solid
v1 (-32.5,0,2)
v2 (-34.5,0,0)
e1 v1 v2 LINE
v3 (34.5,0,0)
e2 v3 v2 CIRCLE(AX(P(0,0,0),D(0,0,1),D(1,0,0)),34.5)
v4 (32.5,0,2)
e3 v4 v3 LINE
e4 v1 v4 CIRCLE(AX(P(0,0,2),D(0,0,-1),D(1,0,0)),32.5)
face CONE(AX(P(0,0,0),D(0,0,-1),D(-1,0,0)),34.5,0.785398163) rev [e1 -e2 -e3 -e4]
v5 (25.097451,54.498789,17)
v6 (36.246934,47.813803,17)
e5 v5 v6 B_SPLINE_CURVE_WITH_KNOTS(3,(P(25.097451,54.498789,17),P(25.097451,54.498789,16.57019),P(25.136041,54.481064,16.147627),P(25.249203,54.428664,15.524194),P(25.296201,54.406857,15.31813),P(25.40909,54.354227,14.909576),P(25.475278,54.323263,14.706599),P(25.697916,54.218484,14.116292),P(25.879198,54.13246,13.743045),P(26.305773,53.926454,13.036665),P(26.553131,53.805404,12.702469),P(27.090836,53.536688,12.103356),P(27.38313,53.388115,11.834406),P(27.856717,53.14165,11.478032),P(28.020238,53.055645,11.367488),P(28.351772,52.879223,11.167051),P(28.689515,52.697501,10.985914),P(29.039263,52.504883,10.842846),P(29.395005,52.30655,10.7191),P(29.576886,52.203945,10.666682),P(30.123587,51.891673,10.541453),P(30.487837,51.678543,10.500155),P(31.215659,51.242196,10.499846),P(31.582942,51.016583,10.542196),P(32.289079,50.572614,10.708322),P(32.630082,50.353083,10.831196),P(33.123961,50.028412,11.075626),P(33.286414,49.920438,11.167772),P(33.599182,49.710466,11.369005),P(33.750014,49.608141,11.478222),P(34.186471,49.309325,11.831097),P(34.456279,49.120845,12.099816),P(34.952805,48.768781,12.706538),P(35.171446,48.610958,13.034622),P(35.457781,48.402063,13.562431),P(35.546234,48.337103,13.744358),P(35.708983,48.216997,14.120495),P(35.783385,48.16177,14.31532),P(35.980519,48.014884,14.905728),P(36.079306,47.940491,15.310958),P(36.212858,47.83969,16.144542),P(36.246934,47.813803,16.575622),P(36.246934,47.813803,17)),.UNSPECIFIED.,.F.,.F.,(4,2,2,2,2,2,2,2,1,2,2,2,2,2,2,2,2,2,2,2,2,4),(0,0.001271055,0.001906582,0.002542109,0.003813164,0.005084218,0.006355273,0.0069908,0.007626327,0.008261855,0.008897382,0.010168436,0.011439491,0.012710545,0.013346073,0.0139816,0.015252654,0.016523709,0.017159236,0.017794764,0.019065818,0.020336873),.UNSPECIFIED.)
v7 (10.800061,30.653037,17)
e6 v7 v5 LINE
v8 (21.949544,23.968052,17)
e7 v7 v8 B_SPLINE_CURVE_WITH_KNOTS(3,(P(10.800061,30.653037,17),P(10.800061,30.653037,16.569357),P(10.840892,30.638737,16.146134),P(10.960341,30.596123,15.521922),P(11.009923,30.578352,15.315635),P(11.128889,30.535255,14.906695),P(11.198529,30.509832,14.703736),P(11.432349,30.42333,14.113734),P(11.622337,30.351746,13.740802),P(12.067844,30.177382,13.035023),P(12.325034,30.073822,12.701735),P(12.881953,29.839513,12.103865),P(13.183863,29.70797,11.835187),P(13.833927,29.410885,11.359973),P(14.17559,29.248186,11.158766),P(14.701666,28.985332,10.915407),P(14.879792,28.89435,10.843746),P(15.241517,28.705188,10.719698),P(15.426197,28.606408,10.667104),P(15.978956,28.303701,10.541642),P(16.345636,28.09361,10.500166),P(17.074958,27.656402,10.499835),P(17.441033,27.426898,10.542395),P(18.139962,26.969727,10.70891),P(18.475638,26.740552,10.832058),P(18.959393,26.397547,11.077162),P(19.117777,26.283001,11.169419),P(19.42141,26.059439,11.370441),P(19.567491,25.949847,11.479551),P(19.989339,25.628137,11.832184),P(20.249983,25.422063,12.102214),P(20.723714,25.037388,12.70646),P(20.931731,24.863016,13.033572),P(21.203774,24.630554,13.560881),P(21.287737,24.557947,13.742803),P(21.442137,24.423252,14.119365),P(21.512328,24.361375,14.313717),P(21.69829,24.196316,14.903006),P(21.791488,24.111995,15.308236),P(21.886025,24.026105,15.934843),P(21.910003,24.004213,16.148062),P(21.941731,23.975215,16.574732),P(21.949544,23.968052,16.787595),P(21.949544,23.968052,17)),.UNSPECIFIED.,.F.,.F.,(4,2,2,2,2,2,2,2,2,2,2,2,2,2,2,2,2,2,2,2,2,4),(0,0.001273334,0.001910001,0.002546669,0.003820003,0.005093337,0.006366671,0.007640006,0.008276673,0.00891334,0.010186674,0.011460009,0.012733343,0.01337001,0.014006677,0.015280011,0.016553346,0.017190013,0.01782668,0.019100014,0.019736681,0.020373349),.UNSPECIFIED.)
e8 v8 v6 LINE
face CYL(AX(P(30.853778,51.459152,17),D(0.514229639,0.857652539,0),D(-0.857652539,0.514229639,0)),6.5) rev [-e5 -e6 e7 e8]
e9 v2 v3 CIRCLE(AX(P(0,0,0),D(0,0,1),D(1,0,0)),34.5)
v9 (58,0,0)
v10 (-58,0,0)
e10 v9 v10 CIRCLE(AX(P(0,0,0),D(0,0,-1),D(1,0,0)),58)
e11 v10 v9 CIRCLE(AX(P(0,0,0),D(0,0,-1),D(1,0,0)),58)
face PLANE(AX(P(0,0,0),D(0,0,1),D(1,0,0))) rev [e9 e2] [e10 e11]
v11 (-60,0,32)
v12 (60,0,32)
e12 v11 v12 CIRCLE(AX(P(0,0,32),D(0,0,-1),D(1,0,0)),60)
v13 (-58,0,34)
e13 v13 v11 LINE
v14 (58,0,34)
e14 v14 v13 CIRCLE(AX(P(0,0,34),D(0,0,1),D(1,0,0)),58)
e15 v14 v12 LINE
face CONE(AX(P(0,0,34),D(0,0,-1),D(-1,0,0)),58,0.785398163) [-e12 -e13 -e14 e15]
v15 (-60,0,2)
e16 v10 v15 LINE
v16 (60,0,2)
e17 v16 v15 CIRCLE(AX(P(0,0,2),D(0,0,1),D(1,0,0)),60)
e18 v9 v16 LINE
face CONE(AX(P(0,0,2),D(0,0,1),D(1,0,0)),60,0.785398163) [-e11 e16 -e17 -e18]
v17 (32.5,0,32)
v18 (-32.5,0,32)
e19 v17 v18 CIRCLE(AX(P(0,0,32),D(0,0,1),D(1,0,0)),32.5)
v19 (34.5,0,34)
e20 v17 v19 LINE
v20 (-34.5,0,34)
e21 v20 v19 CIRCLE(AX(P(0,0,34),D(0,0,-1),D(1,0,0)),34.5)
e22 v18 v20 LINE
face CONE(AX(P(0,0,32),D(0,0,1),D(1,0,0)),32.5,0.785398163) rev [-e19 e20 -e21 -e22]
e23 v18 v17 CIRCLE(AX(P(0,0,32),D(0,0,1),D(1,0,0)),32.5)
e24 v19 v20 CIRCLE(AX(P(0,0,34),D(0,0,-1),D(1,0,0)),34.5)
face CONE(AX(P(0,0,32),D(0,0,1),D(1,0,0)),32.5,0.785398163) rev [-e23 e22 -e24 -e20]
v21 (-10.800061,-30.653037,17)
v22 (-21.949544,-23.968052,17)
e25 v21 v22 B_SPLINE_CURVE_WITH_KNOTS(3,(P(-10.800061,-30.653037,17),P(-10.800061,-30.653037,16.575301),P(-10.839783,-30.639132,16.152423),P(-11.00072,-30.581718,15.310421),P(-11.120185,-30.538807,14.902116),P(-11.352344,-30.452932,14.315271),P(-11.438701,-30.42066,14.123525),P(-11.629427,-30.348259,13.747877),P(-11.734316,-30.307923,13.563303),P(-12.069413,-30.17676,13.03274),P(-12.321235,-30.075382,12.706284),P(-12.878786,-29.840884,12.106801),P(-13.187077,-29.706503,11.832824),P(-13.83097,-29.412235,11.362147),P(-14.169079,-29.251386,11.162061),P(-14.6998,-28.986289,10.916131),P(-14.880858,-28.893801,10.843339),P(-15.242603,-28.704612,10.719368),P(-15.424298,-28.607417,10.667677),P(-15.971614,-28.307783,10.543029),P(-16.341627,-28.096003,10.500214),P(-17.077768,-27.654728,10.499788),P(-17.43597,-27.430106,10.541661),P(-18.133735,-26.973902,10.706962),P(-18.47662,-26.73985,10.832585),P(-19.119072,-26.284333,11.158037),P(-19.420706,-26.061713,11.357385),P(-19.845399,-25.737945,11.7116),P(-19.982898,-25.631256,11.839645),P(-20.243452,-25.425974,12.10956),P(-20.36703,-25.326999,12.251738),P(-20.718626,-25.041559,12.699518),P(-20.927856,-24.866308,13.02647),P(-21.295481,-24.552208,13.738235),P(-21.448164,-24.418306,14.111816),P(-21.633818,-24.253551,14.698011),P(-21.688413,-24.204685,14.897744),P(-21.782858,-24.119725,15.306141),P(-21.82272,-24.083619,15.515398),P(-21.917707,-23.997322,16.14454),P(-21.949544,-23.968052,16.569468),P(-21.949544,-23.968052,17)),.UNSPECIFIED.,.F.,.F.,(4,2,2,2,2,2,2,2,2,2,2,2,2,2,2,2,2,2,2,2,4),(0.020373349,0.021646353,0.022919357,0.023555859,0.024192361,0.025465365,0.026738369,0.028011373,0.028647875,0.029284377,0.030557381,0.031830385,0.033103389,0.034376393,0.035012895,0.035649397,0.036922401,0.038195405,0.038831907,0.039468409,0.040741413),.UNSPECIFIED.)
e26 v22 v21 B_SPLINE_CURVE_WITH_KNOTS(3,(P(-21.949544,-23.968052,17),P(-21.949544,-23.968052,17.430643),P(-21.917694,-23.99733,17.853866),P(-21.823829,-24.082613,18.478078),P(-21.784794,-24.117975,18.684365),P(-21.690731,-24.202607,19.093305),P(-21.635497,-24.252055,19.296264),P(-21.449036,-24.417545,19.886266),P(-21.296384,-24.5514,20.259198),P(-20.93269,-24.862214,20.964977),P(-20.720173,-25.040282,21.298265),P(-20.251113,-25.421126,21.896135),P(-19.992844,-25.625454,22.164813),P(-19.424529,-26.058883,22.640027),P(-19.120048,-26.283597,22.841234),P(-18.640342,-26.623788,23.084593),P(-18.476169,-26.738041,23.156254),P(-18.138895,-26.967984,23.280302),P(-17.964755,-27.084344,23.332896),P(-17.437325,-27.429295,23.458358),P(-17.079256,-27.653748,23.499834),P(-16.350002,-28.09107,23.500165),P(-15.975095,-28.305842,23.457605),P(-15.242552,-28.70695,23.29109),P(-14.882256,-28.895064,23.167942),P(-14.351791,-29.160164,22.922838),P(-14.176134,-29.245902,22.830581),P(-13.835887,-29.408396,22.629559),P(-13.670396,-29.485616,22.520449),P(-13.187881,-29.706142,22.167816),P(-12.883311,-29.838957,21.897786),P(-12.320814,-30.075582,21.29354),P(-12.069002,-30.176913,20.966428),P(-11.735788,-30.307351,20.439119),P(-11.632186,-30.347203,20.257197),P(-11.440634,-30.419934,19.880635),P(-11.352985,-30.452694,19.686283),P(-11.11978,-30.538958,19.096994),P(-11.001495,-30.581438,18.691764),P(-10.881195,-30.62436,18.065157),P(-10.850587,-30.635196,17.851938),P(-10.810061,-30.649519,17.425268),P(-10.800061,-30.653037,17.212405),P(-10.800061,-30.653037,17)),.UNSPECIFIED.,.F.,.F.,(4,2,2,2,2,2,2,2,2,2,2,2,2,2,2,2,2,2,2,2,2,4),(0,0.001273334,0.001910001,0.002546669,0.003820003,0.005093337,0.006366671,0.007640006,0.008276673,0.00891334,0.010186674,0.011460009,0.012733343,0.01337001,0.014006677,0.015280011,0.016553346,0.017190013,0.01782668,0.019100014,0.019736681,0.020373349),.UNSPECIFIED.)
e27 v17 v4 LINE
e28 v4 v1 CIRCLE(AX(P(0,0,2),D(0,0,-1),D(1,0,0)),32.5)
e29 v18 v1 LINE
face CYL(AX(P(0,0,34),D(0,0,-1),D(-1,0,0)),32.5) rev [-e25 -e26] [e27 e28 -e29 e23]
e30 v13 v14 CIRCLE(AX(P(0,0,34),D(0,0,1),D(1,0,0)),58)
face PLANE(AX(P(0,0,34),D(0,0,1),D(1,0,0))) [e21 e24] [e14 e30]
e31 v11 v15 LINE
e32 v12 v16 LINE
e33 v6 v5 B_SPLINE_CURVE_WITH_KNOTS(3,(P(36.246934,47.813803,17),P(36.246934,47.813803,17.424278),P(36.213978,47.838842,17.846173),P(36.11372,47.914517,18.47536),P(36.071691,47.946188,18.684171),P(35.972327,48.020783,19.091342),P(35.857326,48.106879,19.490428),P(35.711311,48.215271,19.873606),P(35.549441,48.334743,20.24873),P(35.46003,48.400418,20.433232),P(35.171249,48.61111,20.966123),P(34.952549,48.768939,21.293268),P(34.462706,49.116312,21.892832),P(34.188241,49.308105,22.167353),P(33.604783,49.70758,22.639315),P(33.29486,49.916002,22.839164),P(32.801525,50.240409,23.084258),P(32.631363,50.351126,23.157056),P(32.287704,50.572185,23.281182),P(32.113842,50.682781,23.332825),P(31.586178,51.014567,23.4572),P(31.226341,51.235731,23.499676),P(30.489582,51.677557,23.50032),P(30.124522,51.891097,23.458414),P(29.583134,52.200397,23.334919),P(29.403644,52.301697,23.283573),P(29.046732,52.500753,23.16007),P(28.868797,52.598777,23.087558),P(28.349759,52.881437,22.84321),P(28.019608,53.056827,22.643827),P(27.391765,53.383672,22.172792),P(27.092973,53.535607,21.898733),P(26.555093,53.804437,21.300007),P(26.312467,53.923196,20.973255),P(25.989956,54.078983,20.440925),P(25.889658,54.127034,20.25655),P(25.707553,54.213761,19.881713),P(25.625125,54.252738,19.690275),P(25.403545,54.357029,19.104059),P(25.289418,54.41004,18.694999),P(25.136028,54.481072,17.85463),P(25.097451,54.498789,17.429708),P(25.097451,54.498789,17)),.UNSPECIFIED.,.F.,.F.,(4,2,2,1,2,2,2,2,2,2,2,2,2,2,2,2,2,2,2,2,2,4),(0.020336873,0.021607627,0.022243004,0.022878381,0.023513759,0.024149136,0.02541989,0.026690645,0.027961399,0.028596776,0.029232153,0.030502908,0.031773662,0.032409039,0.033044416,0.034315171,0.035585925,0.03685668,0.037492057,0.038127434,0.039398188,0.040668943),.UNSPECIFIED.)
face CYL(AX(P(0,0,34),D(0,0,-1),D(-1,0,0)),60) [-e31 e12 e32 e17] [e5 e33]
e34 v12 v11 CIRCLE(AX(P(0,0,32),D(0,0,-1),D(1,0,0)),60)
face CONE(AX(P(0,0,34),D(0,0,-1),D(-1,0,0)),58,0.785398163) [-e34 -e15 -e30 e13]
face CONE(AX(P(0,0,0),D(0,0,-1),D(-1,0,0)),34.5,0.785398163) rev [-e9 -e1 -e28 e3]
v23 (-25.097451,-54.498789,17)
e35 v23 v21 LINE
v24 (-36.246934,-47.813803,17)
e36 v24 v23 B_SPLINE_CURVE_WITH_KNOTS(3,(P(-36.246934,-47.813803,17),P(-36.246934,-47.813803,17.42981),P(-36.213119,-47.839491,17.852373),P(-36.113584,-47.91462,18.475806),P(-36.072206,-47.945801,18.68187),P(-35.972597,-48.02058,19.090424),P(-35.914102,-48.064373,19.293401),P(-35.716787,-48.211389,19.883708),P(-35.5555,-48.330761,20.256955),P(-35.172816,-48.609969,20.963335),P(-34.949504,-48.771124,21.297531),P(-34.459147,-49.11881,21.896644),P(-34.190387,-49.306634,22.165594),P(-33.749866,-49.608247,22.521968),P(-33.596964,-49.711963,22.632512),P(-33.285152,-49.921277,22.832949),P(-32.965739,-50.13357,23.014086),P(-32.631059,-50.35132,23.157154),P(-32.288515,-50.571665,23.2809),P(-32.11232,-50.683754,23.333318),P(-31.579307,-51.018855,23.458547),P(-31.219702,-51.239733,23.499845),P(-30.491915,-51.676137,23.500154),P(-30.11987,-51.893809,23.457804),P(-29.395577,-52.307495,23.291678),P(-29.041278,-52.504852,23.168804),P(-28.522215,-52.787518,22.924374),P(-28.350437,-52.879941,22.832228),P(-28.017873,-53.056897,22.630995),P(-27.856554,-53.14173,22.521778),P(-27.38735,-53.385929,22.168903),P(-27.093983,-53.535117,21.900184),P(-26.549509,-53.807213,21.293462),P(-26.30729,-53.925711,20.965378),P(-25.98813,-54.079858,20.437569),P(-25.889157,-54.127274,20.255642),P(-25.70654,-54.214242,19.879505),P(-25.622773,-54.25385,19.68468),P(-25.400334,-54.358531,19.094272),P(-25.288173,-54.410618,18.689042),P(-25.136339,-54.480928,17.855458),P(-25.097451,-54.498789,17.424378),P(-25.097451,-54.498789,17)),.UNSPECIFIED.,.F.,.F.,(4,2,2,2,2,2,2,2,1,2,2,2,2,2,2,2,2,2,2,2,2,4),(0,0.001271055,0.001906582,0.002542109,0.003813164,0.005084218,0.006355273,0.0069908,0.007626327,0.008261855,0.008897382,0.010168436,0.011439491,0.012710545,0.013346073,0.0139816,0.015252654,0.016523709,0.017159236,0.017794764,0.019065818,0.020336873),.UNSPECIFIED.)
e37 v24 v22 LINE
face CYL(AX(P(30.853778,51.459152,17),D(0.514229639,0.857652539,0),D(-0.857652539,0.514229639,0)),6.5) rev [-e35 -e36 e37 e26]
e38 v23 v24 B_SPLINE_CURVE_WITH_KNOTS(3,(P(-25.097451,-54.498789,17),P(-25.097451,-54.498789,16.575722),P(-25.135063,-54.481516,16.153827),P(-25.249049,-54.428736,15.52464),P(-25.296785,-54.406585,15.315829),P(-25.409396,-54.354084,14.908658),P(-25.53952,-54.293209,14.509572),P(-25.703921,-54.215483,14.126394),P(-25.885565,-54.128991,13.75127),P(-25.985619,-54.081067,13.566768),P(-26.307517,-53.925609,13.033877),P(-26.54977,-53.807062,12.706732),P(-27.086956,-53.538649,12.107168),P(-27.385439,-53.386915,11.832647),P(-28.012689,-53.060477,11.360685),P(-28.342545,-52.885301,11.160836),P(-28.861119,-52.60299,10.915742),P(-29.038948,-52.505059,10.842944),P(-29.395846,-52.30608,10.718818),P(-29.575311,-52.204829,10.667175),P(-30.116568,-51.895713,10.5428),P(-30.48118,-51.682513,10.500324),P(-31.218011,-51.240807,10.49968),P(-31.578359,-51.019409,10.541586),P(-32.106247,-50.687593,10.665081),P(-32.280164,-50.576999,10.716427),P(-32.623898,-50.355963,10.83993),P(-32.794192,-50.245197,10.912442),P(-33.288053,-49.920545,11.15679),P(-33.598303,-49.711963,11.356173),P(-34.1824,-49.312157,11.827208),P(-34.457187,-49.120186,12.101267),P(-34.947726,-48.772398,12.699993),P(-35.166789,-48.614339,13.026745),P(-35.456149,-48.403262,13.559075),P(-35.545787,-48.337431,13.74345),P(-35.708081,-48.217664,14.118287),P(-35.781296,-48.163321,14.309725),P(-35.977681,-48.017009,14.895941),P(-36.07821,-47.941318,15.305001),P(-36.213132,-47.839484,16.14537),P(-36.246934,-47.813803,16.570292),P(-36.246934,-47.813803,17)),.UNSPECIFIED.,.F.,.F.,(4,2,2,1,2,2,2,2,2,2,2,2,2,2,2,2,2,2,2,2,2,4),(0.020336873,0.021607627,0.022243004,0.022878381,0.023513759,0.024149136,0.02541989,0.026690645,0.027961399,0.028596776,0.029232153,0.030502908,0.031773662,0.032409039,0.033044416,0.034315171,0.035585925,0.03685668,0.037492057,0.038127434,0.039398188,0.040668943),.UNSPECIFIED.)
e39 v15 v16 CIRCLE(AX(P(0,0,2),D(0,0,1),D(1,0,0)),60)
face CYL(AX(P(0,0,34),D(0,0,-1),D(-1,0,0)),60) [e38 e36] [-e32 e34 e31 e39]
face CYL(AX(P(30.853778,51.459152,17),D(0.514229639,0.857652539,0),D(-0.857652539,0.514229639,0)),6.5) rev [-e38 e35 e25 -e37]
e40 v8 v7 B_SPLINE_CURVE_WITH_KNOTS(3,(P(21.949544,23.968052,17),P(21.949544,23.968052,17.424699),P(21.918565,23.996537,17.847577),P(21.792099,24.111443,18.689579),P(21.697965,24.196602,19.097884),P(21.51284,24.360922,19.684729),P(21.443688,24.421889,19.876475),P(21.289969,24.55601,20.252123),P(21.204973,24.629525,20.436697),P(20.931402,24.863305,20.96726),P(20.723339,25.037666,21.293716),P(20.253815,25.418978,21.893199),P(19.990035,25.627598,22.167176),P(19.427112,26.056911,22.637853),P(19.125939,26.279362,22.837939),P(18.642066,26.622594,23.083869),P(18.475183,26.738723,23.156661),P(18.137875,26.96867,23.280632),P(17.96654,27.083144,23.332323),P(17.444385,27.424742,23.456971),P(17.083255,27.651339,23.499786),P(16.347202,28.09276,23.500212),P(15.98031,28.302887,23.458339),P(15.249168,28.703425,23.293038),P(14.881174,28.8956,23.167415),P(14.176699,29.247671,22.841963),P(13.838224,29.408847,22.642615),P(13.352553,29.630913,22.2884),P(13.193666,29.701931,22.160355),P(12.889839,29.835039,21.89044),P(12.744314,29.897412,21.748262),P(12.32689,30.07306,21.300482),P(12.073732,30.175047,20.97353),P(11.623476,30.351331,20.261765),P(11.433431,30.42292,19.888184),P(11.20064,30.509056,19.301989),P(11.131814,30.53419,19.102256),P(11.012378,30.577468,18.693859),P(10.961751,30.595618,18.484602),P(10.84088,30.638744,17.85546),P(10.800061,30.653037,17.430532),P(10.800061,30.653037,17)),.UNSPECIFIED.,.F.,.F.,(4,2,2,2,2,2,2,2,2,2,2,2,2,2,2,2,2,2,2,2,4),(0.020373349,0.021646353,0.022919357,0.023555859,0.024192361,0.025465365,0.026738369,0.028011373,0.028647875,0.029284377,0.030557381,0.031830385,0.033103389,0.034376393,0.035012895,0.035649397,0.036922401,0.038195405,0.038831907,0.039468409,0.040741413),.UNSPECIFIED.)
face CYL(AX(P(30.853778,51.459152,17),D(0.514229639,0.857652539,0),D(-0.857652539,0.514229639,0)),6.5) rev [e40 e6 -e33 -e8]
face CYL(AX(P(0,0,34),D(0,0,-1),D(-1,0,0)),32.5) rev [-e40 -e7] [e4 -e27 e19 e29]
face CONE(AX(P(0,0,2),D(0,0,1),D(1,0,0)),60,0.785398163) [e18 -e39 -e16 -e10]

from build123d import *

# Parameters (mm, degrees)
SKETCH1_R                  = 60
SKETCH1_R_2                = 32.5
BOSS_EXTRUDE1_DEPTH        = 34
F_13_0_13_DIAMETER_HOLE1_D = 13
CHAMFER1_SIZE              = 2


with BuildPart() as part:
    # Sketch1 → Boss-Extrude1 (new body)
    with BuildSketch(Plane.XY):
        Circle(SKETCH1_R)
        Circle(SKETCH1_R_2, mode=Mode.SUBTRACT)
    extrude(amount=BOSS_EXTRUDE1_DEPTH)

    # Ø13.0 (13) Diameter Hole1 (through all)
    with Locations(Plane(origin=(30.853778368, 51.459152348, 17), x_dir=(0.85765253914, -0.514229639467, 0), z_dir=(0.514229639467, 0.85765253914, 0))):
        with Locations((0, 0)):
            Hole(F_13_0_13_DIAMETER_HOLE1_D / 2)

    # Chamfer1
    chamfer1_edges = [part.edges().sort_by_distance(p)[0] for p in [
        (-60, 0, 0),
        (-60, 0, 34),
        (-32.5, 0, 0),
        (-32.5, 0, 34),
    ]]
    chamfer(chamfer1_edges, length=CHAMFER1_SIZE)


solid = part.part
